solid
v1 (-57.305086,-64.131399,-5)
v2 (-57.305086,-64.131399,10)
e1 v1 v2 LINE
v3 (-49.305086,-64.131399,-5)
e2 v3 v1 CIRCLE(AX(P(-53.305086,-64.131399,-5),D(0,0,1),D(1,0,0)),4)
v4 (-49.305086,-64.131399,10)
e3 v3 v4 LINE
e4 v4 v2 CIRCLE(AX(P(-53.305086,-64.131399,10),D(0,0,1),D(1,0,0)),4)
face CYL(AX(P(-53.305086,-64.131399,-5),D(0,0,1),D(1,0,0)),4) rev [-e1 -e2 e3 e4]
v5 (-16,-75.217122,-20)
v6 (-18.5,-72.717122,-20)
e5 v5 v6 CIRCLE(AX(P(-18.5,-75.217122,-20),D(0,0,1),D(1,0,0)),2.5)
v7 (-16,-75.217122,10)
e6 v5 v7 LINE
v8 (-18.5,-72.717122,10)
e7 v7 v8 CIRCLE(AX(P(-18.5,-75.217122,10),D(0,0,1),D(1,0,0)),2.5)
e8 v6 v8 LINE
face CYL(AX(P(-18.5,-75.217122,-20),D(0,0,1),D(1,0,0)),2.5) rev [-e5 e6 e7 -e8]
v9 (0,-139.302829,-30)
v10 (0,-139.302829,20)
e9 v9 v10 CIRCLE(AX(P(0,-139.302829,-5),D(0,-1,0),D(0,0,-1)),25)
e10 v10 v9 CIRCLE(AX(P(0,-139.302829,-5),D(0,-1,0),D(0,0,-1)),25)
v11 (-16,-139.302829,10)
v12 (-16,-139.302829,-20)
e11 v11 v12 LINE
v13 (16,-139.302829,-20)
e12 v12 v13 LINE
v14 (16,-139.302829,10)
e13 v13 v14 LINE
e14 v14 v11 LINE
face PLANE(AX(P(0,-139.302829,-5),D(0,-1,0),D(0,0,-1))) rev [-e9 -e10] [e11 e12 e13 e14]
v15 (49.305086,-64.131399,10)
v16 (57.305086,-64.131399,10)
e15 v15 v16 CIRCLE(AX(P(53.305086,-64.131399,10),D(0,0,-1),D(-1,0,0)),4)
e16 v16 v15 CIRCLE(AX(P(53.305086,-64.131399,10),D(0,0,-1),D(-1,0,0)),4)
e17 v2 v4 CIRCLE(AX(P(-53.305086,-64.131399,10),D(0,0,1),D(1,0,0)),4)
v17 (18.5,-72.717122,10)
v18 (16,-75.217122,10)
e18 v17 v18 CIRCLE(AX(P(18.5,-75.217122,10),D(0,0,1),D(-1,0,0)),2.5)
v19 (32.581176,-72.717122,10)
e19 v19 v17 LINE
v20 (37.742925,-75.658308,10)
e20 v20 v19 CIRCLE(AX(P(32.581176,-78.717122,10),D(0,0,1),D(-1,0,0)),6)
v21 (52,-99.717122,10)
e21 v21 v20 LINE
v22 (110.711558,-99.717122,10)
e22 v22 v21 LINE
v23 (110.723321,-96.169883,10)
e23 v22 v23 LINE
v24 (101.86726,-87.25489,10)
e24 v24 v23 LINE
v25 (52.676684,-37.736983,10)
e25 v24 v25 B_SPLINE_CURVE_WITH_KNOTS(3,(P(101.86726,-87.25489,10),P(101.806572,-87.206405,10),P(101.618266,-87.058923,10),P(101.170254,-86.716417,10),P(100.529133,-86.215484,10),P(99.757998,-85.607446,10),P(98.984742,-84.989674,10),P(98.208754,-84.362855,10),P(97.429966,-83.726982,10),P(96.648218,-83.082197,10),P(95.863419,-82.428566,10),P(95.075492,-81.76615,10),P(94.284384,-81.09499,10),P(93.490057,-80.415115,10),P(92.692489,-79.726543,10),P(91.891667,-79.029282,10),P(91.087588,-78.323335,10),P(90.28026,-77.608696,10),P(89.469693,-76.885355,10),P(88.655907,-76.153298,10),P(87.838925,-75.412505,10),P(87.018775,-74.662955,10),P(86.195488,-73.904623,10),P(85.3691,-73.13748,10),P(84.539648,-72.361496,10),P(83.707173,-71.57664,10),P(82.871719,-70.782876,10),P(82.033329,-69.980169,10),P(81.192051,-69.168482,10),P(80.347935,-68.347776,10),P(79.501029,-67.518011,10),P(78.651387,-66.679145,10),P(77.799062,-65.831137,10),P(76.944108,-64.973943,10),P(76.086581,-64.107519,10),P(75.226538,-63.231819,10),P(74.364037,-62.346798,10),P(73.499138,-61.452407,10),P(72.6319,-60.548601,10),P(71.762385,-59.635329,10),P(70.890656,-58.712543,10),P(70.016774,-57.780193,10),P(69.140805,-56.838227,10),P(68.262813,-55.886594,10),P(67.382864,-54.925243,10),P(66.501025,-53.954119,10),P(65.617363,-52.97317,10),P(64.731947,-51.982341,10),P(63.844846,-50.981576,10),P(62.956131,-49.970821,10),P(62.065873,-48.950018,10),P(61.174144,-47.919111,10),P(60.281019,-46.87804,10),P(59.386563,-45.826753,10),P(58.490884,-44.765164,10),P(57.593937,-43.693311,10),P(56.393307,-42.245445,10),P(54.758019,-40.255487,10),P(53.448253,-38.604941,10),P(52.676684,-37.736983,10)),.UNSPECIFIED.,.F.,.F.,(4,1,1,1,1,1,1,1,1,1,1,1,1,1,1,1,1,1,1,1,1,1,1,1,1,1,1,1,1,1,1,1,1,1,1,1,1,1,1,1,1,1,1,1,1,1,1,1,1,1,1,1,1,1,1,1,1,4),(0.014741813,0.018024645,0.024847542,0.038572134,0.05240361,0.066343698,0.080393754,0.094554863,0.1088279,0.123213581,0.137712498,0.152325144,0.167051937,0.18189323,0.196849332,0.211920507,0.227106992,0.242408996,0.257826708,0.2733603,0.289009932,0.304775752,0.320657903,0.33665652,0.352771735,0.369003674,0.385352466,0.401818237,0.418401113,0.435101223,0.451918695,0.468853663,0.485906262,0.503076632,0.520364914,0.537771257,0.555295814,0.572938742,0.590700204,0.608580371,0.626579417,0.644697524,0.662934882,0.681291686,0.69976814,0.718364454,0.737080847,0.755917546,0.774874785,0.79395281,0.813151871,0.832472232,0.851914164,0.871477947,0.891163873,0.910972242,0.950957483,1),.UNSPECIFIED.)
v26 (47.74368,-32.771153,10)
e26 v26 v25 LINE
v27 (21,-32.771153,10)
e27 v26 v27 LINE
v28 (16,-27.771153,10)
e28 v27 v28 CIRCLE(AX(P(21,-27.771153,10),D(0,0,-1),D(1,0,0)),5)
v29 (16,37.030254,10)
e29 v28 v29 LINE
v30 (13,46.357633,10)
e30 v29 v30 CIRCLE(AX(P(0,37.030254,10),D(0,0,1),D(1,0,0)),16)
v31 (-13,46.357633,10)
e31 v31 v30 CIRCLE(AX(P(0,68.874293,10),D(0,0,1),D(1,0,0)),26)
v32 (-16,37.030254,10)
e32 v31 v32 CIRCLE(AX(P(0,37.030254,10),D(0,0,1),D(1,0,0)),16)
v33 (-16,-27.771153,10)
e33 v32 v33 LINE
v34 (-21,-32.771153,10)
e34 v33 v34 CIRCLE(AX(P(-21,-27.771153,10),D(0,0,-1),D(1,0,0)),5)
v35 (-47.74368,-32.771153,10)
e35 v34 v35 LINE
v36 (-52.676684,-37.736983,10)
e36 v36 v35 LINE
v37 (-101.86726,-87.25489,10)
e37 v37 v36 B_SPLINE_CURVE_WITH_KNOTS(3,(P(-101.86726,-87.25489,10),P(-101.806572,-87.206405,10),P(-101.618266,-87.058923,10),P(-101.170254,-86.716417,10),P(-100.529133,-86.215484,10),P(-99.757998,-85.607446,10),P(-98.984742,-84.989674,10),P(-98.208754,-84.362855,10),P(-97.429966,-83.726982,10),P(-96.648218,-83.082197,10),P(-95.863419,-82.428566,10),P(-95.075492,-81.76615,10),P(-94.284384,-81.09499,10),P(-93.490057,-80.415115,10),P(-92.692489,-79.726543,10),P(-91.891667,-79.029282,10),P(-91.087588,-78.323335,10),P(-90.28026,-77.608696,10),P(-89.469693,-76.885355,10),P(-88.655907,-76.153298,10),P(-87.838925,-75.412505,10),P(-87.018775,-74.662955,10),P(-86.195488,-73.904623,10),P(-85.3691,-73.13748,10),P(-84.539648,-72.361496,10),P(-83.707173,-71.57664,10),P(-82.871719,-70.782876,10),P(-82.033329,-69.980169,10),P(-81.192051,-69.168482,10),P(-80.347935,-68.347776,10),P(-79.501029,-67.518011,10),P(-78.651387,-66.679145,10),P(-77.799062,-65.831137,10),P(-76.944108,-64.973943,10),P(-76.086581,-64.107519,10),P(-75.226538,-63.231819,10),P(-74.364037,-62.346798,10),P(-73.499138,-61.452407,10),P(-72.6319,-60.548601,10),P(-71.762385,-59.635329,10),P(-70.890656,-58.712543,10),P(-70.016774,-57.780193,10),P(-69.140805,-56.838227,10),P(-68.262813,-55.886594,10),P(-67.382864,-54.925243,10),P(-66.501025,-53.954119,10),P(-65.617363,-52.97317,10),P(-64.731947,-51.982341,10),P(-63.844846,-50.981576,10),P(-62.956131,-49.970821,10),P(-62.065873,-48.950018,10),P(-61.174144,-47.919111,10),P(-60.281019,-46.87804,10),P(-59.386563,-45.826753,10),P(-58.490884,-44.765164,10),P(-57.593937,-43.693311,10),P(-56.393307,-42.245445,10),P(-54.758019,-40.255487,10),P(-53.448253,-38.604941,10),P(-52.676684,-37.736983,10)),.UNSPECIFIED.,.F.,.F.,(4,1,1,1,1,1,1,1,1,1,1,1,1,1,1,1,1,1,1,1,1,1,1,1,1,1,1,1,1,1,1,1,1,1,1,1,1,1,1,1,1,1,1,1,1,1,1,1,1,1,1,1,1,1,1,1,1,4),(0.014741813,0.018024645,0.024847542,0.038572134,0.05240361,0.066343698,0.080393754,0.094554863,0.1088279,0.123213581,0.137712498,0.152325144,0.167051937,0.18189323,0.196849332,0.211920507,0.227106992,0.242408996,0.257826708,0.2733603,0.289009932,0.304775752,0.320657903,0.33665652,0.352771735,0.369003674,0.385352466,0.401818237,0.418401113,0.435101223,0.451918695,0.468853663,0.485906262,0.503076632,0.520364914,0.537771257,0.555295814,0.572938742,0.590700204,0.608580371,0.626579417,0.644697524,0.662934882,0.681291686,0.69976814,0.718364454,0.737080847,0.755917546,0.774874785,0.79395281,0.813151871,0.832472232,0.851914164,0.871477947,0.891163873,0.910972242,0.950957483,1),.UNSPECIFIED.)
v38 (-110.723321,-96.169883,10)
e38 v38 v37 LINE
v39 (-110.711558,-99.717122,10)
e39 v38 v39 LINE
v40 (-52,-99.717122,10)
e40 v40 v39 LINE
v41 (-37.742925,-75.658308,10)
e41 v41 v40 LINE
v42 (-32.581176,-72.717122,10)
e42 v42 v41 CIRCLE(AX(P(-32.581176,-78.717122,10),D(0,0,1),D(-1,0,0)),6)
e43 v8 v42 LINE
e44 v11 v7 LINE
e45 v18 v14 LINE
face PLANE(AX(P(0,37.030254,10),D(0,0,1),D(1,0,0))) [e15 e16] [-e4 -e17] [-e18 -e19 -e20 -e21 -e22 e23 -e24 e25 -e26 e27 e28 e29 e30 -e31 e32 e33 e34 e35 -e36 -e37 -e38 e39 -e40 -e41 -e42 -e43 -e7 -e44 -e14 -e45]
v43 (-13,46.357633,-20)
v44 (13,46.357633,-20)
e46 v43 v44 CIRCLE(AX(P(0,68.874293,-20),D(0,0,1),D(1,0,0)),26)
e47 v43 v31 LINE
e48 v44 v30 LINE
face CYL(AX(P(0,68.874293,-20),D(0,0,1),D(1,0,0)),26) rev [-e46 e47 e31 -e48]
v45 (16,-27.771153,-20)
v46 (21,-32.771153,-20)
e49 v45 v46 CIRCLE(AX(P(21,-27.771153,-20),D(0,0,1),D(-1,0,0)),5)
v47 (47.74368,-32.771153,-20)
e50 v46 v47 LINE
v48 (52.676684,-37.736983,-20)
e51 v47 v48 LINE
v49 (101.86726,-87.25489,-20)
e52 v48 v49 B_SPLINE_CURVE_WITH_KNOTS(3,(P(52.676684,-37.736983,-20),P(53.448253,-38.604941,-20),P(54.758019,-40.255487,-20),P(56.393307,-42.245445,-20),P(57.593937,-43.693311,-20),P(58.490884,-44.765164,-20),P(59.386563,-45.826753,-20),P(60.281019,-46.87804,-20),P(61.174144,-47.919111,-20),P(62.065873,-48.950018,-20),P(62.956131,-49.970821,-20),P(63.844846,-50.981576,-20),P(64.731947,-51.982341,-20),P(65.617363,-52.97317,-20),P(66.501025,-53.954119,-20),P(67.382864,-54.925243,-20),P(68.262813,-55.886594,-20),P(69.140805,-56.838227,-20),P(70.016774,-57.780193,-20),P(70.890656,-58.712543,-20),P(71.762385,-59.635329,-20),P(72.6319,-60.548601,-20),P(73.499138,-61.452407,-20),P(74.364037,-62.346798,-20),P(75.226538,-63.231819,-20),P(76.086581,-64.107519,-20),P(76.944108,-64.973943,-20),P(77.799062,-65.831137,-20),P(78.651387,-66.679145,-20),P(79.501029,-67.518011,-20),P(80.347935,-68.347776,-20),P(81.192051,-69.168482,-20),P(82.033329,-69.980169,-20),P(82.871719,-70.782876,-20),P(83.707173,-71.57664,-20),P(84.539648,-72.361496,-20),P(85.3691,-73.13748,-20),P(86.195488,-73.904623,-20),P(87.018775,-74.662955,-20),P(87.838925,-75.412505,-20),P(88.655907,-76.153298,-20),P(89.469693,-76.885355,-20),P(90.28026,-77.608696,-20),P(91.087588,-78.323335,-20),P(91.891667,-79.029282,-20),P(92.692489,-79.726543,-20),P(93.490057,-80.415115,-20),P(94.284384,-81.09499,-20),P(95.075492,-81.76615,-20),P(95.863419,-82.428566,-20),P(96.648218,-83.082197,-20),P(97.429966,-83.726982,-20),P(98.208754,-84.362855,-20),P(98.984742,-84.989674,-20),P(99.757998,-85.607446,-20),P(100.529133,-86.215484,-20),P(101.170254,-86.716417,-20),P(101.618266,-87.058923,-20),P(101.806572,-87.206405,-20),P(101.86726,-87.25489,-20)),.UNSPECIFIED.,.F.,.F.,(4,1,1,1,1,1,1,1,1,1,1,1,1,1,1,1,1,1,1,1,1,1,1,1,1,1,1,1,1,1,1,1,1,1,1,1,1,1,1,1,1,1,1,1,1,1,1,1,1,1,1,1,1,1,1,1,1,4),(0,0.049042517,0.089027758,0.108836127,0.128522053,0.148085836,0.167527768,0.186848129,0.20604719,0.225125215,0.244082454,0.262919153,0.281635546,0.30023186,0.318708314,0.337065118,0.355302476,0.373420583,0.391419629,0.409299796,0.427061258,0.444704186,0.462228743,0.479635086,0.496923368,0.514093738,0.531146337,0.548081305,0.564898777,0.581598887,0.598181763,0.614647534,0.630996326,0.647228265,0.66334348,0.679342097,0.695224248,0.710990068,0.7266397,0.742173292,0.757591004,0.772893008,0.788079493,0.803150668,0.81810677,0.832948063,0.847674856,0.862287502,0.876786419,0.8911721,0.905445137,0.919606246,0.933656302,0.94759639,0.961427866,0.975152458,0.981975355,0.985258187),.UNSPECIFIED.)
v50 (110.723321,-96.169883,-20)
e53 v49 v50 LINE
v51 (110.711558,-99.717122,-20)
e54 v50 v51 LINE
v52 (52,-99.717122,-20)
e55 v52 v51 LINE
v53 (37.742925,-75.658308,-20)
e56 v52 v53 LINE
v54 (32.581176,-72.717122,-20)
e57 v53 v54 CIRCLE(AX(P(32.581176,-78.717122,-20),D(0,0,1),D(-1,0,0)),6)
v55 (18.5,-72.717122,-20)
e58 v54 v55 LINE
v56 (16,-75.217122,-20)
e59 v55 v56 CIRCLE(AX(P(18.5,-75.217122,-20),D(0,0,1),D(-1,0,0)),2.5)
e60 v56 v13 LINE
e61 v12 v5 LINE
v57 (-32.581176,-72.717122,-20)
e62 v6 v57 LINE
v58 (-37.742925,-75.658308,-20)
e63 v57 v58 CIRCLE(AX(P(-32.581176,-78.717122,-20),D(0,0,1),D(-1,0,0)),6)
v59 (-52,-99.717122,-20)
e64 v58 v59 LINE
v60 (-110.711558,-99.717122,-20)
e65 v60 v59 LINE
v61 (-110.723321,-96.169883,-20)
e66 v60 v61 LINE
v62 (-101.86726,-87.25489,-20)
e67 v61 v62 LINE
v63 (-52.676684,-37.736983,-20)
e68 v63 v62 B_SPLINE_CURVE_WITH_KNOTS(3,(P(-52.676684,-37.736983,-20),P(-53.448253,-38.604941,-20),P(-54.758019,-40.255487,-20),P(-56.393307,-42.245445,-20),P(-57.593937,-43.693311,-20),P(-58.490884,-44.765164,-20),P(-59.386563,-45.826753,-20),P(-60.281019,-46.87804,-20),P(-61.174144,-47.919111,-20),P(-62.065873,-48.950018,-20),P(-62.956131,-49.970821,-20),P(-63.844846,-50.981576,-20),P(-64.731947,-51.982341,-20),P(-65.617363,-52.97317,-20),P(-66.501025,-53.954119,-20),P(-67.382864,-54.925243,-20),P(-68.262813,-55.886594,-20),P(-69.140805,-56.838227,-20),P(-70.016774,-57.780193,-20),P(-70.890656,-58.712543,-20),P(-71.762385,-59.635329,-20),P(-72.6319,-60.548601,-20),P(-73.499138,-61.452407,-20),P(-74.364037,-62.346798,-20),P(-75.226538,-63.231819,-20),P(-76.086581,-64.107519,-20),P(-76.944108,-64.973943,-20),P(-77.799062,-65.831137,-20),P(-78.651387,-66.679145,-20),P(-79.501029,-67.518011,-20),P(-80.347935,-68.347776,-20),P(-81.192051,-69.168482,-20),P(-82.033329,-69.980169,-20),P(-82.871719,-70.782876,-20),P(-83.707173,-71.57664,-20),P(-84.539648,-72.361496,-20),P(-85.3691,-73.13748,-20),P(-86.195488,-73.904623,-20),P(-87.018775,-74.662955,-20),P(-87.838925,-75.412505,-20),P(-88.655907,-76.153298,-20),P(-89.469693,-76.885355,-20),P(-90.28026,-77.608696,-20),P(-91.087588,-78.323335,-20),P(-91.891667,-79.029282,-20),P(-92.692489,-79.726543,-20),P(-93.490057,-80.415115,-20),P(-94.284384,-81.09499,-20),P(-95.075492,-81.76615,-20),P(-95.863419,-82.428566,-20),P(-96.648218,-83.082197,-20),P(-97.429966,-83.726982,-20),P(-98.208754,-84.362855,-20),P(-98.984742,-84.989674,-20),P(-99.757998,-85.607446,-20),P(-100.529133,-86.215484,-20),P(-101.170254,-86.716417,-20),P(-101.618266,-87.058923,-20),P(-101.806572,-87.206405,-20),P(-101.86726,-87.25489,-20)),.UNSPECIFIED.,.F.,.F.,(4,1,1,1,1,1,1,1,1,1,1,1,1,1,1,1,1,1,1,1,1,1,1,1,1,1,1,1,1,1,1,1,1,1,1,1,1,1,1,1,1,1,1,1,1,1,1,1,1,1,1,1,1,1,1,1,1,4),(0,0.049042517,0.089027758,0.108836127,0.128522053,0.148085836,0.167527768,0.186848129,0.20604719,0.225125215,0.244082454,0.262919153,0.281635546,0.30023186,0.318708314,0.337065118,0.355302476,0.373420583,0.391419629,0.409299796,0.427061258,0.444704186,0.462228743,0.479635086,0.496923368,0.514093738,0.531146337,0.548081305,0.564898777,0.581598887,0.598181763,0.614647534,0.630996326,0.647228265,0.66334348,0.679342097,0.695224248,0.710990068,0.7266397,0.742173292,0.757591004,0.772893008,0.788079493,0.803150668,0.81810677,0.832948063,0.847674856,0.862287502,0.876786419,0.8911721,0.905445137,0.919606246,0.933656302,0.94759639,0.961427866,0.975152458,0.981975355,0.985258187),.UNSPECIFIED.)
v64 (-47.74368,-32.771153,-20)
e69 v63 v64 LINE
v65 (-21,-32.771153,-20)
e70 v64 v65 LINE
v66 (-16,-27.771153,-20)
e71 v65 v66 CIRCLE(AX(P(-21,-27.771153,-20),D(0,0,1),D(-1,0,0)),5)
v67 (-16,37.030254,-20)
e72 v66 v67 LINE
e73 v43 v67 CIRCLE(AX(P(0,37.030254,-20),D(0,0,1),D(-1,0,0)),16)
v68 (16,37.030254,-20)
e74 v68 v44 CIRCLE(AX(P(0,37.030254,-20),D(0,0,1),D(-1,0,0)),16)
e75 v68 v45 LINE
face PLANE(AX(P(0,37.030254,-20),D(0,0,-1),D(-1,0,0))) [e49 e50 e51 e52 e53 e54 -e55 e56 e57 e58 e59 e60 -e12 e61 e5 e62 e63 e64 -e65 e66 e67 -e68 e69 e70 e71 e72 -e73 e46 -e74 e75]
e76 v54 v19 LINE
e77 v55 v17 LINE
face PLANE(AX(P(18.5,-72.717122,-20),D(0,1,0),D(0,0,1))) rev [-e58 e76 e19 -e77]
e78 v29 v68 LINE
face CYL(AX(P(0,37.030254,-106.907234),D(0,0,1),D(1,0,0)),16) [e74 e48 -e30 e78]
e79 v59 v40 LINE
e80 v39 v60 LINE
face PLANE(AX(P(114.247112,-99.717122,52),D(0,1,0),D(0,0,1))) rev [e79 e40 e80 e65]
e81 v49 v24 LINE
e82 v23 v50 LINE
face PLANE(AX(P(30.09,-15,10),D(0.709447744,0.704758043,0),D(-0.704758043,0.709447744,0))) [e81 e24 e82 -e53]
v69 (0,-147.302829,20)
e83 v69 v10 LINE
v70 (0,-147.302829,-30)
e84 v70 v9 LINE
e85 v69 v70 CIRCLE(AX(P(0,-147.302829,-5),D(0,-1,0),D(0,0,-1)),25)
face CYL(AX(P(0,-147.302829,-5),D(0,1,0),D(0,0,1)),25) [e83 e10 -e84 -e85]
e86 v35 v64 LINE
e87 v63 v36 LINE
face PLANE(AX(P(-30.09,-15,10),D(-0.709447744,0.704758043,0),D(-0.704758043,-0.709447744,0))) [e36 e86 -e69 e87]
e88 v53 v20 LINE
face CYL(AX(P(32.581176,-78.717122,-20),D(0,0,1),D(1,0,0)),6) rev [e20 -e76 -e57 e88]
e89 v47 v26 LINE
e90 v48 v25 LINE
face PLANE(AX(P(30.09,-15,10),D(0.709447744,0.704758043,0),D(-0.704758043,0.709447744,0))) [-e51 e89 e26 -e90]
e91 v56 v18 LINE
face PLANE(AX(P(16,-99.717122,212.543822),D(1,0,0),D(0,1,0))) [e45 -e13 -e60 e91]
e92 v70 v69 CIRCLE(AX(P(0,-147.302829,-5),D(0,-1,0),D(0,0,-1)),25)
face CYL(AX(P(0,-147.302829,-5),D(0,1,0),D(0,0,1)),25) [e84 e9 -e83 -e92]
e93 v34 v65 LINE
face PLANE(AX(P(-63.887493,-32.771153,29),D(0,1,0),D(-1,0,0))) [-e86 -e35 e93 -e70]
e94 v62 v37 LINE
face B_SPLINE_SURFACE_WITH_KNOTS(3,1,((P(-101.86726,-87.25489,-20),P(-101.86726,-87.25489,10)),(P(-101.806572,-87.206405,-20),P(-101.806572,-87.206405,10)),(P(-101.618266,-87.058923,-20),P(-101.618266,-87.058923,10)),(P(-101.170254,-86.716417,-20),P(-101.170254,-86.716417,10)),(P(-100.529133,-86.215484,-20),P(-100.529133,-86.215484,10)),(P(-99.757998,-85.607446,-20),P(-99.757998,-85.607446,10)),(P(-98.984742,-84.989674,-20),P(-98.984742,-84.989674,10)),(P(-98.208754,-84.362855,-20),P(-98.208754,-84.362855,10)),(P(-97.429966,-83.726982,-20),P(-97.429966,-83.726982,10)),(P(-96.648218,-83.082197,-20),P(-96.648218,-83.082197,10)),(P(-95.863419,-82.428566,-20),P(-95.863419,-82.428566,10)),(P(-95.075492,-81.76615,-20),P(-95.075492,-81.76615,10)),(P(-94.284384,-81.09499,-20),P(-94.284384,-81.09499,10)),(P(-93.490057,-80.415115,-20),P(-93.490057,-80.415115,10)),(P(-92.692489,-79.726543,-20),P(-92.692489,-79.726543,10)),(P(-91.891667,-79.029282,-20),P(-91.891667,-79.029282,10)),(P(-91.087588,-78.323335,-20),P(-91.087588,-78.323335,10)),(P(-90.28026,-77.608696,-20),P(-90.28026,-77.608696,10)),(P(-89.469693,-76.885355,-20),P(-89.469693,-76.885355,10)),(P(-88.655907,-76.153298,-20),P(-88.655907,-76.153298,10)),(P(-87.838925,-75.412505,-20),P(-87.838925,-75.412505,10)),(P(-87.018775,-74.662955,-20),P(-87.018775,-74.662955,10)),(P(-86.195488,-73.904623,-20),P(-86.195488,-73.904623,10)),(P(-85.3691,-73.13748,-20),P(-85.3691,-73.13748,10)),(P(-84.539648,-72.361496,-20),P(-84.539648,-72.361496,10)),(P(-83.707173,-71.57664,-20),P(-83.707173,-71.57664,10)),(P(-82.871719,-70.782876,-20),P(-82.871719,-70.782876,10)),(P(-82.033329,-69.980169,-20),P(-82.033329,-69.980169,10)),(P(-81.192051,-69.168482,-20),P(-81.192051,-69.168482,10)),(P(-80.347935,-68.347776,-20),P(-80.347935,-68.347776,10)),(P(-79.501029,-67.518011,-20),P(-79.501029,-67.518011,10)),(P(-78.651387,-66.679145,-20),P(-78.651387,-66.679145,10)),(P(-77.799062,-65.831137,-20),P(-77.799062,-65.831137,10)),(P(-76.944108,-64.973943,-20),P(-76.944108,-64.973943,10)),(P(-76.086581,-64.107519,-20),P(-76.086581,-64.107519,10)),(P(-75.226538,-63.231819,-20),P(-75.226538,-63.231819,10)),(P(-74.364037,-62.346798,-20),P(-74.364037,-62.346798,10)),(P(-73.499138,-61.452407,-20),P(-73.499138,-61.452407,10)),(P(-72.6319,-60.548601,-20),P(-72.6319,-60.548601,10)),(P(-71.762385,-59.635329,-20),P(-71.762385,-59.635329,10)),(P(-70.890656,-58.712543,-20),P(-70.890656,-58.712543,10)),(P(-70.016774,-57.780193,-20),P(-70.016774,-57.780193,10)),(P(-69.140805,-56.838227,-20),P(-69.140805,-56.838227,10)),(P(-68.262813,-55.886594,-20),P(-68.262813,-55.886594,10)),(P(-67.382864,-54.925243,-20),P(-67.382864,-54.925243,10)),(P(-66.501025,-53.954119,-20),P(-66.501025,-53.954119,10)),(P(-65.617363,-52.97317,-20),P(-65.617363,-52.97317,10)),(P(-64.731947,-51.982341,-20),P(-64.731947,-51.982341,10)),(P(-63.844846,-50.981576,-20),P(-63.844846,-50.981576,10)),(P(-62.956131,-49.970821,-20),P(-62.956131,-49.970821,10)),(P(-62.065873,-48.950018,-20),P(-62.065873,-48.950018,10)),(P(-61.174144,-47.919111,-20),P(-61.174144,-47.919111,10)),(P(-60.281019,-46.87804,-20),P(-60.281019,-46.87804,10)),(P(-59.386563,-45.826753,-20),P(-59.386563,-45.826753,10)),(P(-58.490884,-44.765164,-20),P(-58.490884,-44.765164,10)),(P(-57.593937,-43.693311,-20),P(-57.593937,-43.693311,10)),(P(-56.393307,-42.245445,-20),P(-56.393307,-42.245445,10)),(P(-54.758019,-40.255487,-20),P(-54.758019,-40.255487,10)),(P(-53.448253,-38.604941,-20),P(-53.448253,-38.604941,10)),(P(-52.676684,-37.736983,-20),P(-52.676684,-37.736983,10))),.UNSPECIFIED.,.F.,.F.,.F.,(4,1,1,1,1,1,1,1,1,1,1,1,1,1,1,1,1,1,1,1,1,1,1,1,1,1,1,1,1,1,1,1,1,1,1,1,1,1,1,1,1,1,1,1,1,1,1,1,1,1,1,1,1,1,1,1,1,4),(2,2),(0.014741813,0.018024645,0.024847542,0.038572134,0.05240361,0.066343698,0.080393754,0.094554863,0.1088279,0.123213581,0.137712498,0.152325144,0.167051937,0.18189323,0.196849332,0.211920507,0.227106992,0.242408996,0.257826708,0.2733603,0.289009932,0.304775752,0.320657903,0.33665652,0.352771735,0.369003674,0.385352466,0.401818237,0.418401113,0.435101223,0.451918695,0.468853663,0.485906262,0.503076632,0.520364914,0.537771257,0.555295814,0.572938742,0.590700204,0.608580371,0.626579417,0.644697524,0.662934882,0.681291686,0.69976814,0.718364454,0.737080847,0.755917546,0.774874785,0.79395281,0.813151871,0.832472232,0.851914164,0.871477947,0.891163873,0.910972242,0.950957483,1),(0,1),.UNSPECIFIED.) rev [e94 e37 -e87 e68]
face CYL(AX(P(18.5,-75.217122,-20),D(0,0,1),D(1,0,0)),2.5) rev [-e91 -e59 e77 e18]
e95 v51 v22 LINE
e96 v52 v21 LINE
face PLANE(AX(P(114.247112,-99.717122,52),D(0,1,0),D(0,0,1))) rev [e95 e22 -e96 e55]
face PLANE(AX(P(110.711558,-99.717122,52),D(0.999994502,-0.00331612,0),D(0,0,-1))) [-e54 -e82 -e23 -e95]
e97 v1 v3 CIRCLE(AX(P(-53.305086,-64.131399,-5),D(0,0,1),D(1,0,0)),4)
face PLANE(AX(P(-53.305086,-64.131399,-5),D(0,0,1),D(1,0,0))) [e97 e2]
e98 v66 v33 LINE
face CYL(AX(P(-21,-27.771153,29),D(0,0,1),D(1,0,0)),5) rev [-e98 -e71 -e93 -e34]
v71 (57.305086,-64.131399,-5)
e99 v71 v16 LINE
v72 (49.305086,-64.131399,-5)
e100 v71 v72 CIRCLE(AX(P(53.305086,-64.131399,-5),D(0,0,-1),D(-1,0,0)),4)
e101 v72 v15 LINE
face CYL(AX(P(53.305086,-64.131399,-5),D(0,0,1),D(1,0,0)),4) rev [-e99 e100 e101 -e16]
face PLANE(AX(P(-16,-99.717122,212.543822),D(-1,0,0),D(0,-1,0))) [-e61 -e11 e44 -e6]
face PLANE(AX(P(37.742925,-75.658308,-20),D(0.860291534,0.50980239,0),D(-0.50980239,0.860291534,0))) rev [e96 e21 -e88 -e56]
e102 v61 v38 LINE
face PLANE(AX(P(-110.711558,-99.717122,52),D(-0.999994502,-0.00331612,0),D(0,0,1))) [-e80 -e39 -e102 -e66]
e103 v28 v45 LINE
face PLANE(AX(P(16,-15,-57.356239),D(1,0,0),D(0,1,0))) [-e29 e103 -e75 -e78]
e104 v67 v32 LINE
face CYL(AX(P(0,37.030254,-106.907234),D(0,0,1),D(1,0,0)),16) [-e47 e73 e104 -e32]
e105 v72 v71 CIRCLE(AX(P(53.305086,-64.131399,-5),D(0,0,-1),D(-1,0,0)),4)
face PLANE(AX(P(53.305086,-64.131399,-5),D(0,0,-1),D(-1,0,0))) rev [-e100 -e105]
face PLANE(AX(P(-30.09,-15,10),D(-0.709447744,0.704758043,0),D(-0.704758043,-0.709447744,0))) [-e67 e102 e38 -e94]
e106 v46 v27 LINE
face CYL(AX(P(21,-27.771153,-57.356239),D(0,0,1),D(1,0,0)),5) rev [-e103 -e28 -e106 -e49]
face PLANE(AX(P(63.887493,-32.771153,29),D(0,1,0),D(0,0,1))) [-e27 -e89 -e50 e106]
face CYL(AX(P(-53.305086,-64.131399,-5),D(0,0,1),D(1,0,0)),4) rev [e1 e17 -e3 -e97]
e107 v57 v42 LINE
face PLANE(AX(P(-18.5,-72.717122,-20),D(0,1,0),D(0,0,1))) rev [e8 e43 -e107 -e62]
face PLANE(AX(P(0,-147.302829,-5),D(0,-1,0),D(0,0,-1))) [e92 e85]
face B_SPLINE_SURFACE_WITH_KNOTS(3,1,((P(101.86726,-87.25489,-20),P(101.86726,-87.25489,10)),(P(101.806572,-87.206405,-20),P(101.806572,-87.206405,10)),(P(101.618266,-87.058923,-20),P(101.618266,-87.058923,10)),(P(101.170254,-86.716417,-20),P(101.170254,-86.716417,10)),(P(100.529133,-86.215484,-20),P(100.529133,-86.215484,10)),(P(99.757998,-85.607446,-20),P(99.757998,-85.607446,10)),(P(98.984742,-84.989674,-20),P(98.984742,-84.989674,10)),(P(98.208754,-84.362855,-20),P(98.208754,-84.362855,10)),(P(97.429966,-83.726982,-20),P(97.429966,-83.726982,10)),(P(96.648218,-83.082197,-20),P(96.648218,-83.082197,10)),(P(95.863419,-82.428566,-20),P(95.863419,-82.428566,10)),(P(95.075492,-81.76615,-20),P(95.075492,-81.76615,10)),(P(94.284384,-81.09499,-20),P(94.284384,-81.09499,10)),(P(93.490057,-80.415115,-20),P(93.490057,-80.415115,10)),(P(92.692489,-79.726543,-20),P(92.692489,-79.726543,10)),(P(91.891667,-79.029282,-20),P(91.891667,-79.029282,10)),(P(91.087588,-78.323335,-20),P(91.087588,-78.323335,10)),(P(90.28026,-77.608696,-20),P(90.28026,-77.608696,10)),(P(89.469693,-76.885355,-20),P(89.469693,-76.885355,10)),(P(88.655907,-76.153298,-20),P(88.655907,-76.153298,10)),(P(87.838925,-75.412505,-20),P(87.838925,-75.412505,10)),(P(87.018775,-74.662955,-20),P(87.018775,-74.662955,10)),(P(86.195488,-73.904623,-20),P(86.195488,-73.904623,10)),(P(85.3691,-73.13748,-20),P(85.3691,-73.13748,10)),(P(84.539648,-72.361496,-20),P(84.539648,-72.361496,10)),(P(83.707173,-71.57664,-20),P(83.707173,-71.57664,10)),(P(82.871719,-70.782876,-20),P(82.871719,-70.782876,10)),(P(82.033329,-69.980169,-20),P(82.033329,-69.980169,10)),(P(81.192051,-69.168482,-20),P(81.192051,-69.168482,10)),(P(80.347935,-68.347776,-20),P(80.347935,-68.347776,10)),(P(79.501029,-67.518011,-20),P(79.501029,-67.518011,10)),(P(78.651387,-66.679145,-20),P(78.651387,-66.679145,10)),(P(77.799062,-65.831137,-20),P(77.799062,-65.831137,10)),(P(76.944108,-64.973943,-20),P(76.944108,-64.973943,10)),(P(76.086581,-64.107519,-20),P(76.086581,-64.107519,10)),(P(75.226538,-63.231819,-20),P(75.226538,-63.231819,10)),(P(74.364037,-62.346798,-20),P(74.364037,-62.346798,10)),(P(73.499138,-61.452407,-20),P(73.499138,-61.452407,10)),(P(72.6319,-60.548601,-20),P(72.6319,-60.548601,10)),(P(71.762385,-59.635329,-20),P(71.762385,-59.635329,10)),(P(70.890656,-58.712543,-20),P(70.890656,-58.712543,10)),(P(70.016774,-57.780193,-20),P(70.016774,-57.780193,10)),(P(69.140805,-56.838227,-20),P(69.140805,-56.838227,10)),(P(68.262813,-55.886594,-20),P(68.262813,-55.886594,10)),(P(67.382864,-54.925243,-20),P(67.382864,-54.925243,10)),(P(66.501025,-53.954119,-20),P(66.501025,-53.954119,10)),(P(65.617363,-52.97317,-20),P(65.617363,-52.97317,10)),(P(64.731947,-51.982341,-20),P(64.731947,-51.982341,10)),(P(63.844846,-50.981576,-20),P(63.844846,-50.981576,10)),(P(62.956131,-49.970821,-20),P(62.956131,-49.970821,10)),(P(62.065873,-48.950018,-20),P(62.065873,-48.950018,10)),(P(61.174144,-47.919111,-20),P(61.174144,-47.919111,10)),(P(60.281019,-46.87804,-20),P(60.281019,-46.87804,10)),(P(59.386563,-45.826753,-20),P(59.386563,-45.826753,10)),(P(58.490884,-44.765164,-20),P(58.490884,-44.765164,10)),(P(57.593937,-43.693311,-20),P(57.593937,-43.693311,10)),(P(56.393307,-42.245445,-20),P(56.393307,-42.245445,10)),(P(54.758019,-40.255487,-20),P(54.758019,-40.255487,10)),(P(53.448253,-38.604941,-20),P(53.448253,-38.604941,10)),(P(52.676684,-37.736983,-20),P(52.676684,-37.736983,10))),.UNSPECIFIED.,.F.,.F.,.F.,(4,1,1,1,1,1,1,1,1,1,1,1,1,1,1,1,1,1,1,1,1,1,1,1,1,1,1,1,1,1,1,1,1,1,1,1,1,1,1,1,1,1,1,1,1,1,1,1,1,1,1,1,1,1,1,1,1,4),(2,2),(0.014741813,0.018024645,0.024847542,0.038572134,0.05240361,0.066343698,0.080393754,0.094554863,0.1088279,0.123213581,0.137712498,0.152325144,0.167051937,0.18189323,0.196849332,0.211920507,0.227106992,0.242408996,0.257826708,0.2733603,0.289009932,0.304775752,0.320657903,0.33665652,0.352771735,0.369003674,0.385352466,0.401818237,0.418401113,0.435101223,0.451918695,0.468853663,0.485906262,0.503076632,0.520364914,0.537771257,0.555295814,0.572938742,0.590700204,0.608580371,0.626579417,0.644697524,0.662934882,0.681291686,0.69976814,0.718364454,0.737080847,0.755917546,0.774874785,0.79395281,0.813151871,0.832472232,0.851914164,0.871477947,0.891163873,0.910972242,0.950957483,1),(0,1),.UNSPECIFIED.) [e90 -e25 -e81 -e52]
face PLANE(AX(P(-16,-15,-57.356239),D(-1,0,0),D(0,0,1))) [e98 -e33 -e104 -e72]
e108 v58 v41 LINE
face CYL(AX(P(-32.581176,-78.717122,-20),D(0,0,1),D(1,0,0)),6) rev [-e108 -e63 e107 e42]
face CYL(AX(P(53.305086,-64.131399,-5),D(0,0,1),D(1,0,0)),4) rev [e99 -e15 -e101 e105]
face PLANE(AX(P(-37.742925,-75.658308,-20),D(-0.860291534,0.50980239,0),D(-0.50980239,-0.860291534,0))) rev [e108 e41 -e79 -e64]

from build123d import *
from OCP.BRepFilletAPI import BRepFilletAPI_MakeChamfer

# Parameters (mm, degrees)
BOSS_EXTRUDE1_DEPTH      = 10
BOSS_EXTRUDE2_DEPTH      = 10
SKETCH72_R               = 5
CUT_EXTRUDE2_DEPTH       = 10
CUT_EXTRUDE4_DEPTH       = 14
CUT_EXTRUDE4_DEPTH_BACK  = 19
BOSS_EXTRUDE3_START      = 20
BOSS_EXTRUDE3_DEPTH      = 20
CUT_EXTRUDE5_DEPTH       = 19
CUT_EXTRUDE5_DEPTH_BACK  = 48
SKETCH146_R              = 5
CUT_EXTRUDE6_DEPTH       = 19
CUT_EXTRUDE6_DEPTH_BACK  = 19
CUT_EXTRUDE7_DEPTH       = 60
CUT_EXTRUDE8_DEPTH       = 72
CUT_EXTRUDE9_DEPTH       = 88
BOSS_EXTRUDE6_START      = -7.5
BOSS_EXTRUDE6_DEPTH      = 7.5
CUT_EXTRUDE10_DEPTH      = 19
CUT_EXTRUDE10_DEPTH_BACK = 41
SKETCH171_R              = 5
BOSS_EXTRUDE7_DEPTH      = 7.5
SKETCH172_W              = 3
SKETCH172_H              = 35.030253814
BOSS_EXTRUDE8_DEPTH      = 15
SKETCH173_W              = 32
SKETCH173_H              = 200
BOSS_EXTRUDE9_DEPTH      = 30
CHAMFER1_SIZE            = 5
CHAMFER1_SIZE2           = 3.535553346
FILLET1_R                = 5
CUT_EXTRUDE11_DEPTH      = 30
SKETCH175_W              = 47.76869264
SKETCH175_H              = 185.151923251
CUT_EXTRUDE12_DEPTH      = 55
SKETCH151_R              = 4
CUT_EXTRUDE14_DEPTH      = 15
SKETCH153_R              = 4
CUT_EXTRUDE15_DEPTH      = 15
CHAMFER3_SIZE            = 0.5
BOSS_EXTRUDE10_DEPTH     = 30
CUT_EXTRUDE16_DEPTH      = 181.457563316
SKETCH179_R              = 25
BOSS_EXTRUDE11_DEPTH     = 8


with BuildPart() as part:
    # Sketch1 → Boss-Extrude1 (new body)
    with BuildSketch(Plane.XY):
        with BuildLine():
            Line((-15, 37.030253814), (-15, -127.65801455))
            Line((-15, -127.65801455), (15, -127.65801455))
            Line((15, -127.65801455), (15, 37.030253814))
            ThreePointArc((15, 37.030253814), (0, 52.030253814), (-15, 37.030253814))
        make_face()
    extrude(amount=BOSS_EXTRUDE1_DEPTH)

    # Sketch2 → Boss-Extrude2 (add)
    with BuildSketch(Plane(origin=(0, 0, 0), x_dir=(-1, 0, 0), z_dir=(0, 0, -1))):
        Polygon((0, -15), (30.09, -15), (139.247111701, -124.883480474), (-139.247111701, -124.883480474), (-30.09, -15), align=None)
    extrude(amount=-BOSS_EXTRUDE2_DEPTH)

    # Sketch72 → Cut-Extrude2 (cut)
    with BuildSketch(Plane.XY.offset(10)):
        with Locations((0, 37.030253814)):
            Circle(SKETCH72_R)
    extrude(amount=-CUT_EXTRUDE2_DEPTH, mode=Mode.SUBTRACT)

    # Sketch144 → Cut-Extrude4 (cut, two sides: drawn at the far end of the back side and taken through both)
    with BuildSketch(Plane.XY.offset(10).offset(-CUT_EXTRUDE4_DEPTH_BACK)):
        with BuildLine():
            Line((-13, 37.030253814), (-13, -15))
            Line((-13, -15), (-23, -15))
            Line((-23, -15), (-23, 37.030253814))
            ThreePointArc((-23, 37.030253814), (0, 60.030253814), (23, 37.030253814))
            Line((23, 37.030253814), (23, -15))
            Line((23, -15), (13, -15))
            Line((13, -15), (13, 37.030253814))
            ThreePointArc((13, 37.030253814), (0, 50.030253814), (-13, 37.030253814))
        make_face()
    extrude(amount=CUT_EXTRUDE4_DEPTH + CUT_EXTRUDE4_DEPTH_BACK, mode=Mode.SUBTRACT)

    # Sketch145 → Boss-Extrude3 (add)
    with BuildSketch(Plane(origin=(0, 0, 0), x_dir=(-1, 0, 0), z_dir=(0, 0, -1)).offset(BOSS_EXTRUDE3_START)):
        with BuildLine():
            Line((30.09, -15), (13, -15))
            Line((13, -15), (13, 37.030253814))
            ThreePointArc((13, 37.030253814), (0, 50.030253814), (-13, 37.030253814))
            Line((-13, 37.030253814), (-13, -15))
            Line((-13, -15), (-30.09, -15))
            Line((-30.09, -15), (-139.247111701, -124.883480474))
            Line((-139.247111701, -124.883480474), (-15, -124.883480474))
            Line((-15, -124.883480474), (-15, -127.65801455))
            Line((-15, -127.65801455), (15, -127.65801455))
            Line((15, -127.65801455), (15, -124.883480474))
            Line((15, -124.883480474), (139.247111701, -124.883480474))
            Line((139.247111701, -124.883480474), (30.09, -15))
        make_face()
    extrude(amount=-BOSS_EXTRUDE3_DEPTH)

    # Sketch146 → Cut-Extrude5 (cut, two sides: drawn at the far end of the back side and taken through both)
    with BuildSketch(Plane.XY.offset(-CUT_EXTRUDE5_DEPTH_BACK)):
        with Locations((0, 37.030253814)):
            Circle(SKETCH146_R)
    extrude(amount=CUT_EXTRUDE5_DEPTH + CUT_EXTRUDE5_DEPTH_BACK, mode=Mode.SUBTRACT)

    # Sketch147 → Cut-Extrude6 (cut, two sides: drawn at the far end of the back side and taken through both)
    with BuildSketch(Plane(origin=(0, 0, 0), x_dir=(0, 0, -1), z_dir=(1, 0, 0)).offset(-CUT_EXTRUDE6_DEPTH_BACK)):
        Polygon((-2.5, 50.030253814), (-2.5, 20.030253814), (12.5, 20.030253814), (12.5, 50.030253814), (5, 50.030253814), align=None)
    extrude(amount=CUT_EXTRUDE6_DEPTH + CUT_EXTRUDE6_DEPTH_BACK, mode=Mode.SUBTRACT)

    # Sketch150 → Cut-Extrude7 (cut)
    with BuildSketch(Plane.XY.offset(10)):
        Polygon((-139.247111701, -124.883480474), (-114.247111701, -124.883480474), (-114.247111701, -93.838923463), (-155.604312259, -93.838923463), align=None)
        Polygon((139.247111701, -124.883480474), (114.247111701, -124.883480474), (114.247111701, -93.838923463), (144.778818184, -93.838923463), align=None)
    extrude(amount=-CUT_EXTRUDE7_DEPTH, mode=Mode.SUBTRACT)

    # Sketch155 → Cut-Extrude8 (cut)
    with BuildSketch(Plane(origin=(0, 0, -20), x_dir=(-1, 0, 0), z_dir=(0, 0, -1))):
        Polygon((-114.247111701, -99.71712192), (114.247111701, -99.71712192), (132.998124018, -127.280721413), (-4.838954003, -174.810748317), (-128.945135363, -139.691339549), align=None)
    extrude(amount=-CUT_EXTRUDE8_DEPTH, mode=Mode.SUBTRACT)

    # Sketch168 → Cut-Extrude9 (cut)
    with BuildSketch(Plane.XY.offset(10)):
        with BuildLine():
            Line((-102.627965354, -87.973722378), (-98.21134674, -23.838785425))
            Line((-98.21134674, -23.838785425), (-52.676683547, -37.736983068))
            add(Edge.make_bspline(
                [(-52.676683547, -37.736983068), (-53.448253243, -38.604940944), (-54.758018803, -40.255486938), (-56.393307349, -42.24544513), (-57.59393724, -43.693311358), (-58.490883563, -44.765164273), (-59.386563239, -45.826752691), (-60.281018922, -46.878039923), (-61.174144179, -47.919111167), (-62.065873359, -48.950018312), (-62.956131171, -49.970821146), (-63.844846057, -50.981576429), (-64.731946625, -51.982340808), (-65.617362588, -52.973170047), (-66.501024502, -53.954119244), (-67.382863834, -54.925242774), (-68.262812936, -55.886594308), (-69.140805058, -56.83822681), (-70.016774341, -57.78019253), (-70.890655834, -58.712543006), (-71.762385492, -59.635329052), (-72.6319002, -60.548600748), (-73.499137782, -61.452407427), (-74.36403703, -62.346797658), (-75.226537723, -63.231819226), (-76.086580666, -64.107519102), (-76.944107728, -64.97394342), (-77.799061885, -65.83113743), (-78.651387281, -66.679145464), (-79.501029286, -67.518010878), (-80.347934579, -68.347775997), (-81.192051232, -69.16848204), (-82.033328819, -69.980169042), (-82.871718537, -70.782875754), (-83.707173346, -71.576639531), (-84.539648144, -72.3614962), (-85.369099962, -73.137479905), (-86.195488195, -73.90462292), (-87.018774882, -74.662955436), (-87.838925031, -75.412505303), (-88.655907003, -76.153297726), (-89.469692983, -76.885354899), (-90.280259527, -77.608695576), (-91.08758824, -78.323334537), (-91.89166658, -79.029281964), (-92.692488851, -79.726542658), (-93.490057409, -80.415115104), (-94.284384181, -81.094990278), (-95.075492456, -81.766150286), (-95.86341948, -82.428566214), (-96.6482185, -83.08219705), (-97.429965937, -83.726982263), (-98.208753829, -84.362854554), (-98.984742254, -84.989673948), (-99.757998209, -85.607446121), (-100.529132919, -86.215484264), (-101.170253751, -86.716417382), (-101.895413536, -87.270801703), (-102.35237684, -87.641445426), (-102.627965354, -87.973722378)],
                knots=[0, 0, 0, 0, 0.049042517, 0.089027758, 0.108836127, 0.128522053, 0.148085836, 0.167527768, 0.186848129, 0.20604719, 0.225125215, 0.244082454, 0.262919153, 0.281635546, 0.30023186, 0.318708314, 0.337065118, 0.355302476, 0.373420583, 0.391419629, 0.409299796, 0.427061258, 0.444704186, 0.462228743, 0.479635086, 0.496923368, 0.514093738, 0.531146337, 0.548081305, 0.564898777, 0.581598887, 0.598181763, 0.614647534, 0.630996326, 0.647228265, 0.66334348, 0.679342097, 0.695224248, 0.710990068, 0.7266397, 0.742173292, 0.757591004, 0.772893008, 0.788079493, 0.803150668, 0.81810677, 0.832948063, 0.847674856, 0.862287502, 0.876786419, 0.8911721, 0.905445137, 0.919606246, 0.933656302, 0.94759639, 0.961427866, 0.975152458, 0.981975355, 1, 1, 1, 1], degree=3))
        make_face()
    cut_extrude9 = extrude(amount=-CUT_EXTRUDE9_DEPTH, mode=Mode.SUBTRACT)

    # Mirror1: Cut-Extrude9 across plane
    add(cut_extrude9.mirror(Plane(origin=(0, 0, 0), x_dir=(0, 0, 1), z_dir=(1, 0, 0))), mode=Mode.SUBTRACT)

    # Sketch169 → Boss-Extrude6 (add)
    with BuildSketch(Plane.XY.offset(10).offset(BOSS_EXTRUDE6_START)):
        with BuildLine():
            Line((-16, -15), (-13, -15))
            Line((-13, -15), (-13, 37.030253814))
            ThreePointArc((-13, 37.030253814), (-12.375631297, 41.010674647), (-10.5625, 44.608749295))
            Line((-10.5625, 44.608749295), (-16, 37.030253814))
            Line((-16, 37.030253814), (-16, -15))
        make_face()
        with BuildLine():
            Line((16, -15), (16, 37.030253814))
            Line((16, 37.030253814), (10.5625, 44.608749295))
            ThreePointArc((10.5625, 44.608749295), (12.375631297, 41.010674647), (13, 37.030253814))
            Line((13, 37.030253814), (13, -15))
            Line((13, -15), (16, -15))
        make_face()
    extrude(amount=BOSS_EXTRUDE6_DEPTH)

    # Sketch170 → Cut-Extrude10 (cut, two sides: drawn at the far end of the back side and taken through both)
    with BuildSketch(Plane.XY.offset(10).offset(-CUT_EXTRUDE10_DEPTH_BACK)):
        Polygon((-63.887492501, -32.771153319), (-27.188421499, -2.740818682), (-16, -2.740818682), (-16, -15), (-16, -32.771153319), align=None)
        Polygon((16, -15), (16, -32.771153319), (63.887492501, -32.771153319), (27.188421499, -2.740818682), (16, -2.740818682), align=None)
    extrude(amount=CUT_EXTRUDE10_DEPTH + CUT_EXTRUDE10_DEPTH_BACK, mode=Mode.SUBTRACT)

    # Sketch171 → Boss-Extrude7 (add)
    with BuildSketch(Plane(origin=(0, 0, -20), x_dir=(-1, 0, 0), z_dir=(0, 0, -1))):
        with BuildLine():
            Line((16, -15), (-16, -15))
            Line((-16, -15), (-16, 37.030253814))
            Line((-16, 37.030253814), (-10.5625, 44.608749295))
            ThreePointArc((-10.5625, 44.608749295), (0, 50.030253814), (10.5625, 44.608749295))
            Line((10.5625, 44.608749295), (16, 37.030253814))
            Line((16, 37.030253814), (16, -15))
        make_face()
        with Locations(Location((0, 37.030253814, 0), (0, 0, 180))):
            Circle(SKETCH171_R, mode=Mode.SUBTRACT)
    extrude(amount=-BOSS_EXTRUDE7_DEPTH)

    # Sketch172 → Boss-Extrude8 (add)
    with BuildSketch(Plane(origin=(0, 0, 2.5), x_dir=(-1, 0, 0), z_dir=(0, 0, -1))):
        with Locations((-14.5, 2.515126907)):
            Rectangle(SKETCH172_W, SKETCH172_H)
        with Locations((14.5, 2.515126907)):
            Rectangle(SKETCH172_W, SKETCH172_H)
    extrude(amount=BOSS_EXTRUDE8_DEPTH)

    # Sketch173 → Boss-Extrude9 (add)
    with BuildSketch(Plane(origin=(0, 0, -20), x_dir=(-1, 0, 0), z_dir=(0, 0, -1))):
        with Locations((0, -199.71712192)):
            Rectangle(SKETCH173_W, SKETCH173_H)
    extrude(amount=-BOSS_EXTRUDE9_DEPTH)

    # Chamfer1: one chamfer whose edges measure the first distance from different faces: ONE call of the kernel's chamfer builder (chamfer() names one face for all edges)
    chamfer1_edges_1 = [part.edges().sort_by_distance(p)[0] for p in [
        (-114.247111701, -99.71712192, -5),
    ]]
    chamfer1_side_1 = [part.faces().sort_by_distance(p)[0] for p in [
        (-108.057185848, -93.486006182, -5),
    ]]
    chamfer1_edges_2 = [part.edges().sort_by_distance(p)[0] for p in [
        (114.247111701, -99.71712192, -5),
    ]]
    chamfer1_side_2 = [part.faces().sort_by_distance(p)[0] for p in [
        (108.057185848, -93.486006182, -5),
    ]]
    chamfer1 = BRepFilletAPI_MakeChamfer(part.part.solid().wrapped)
    for e in chamfer1_edges_1:
        chamfer1.Add(CHAMFER1_SIZE, CHAMFER1_SIZE2, e.wrapped, chamfer1_side_1[0].wrapped)  # the first distance lies on this face
    for e in chamfer1_edges_2:
        chamfer1.Add(CHAMFER1_SIZE, CHAMFER1_SIZE2, e.wrapped, chamfer1_side_2[0].wrapped)  # the first distance lies on this face
    add(Compound.cast(chamfer1.Shape()), mode=Mode.REPLACE)

    # Fillet1
    fillet1_edges = [part.edges().sort_by_distance(p)[0] for p in [
        (-16, -32.771153319, -5),
        (16, -32.771153319, -5),
    ]]
    fillet(fillet1_edges, radius=FILLET1_R)

    # Sketch174 → Cut-Extrude11 (cut)
    with BuildSketch(Plane.XY.offset(10)):
        with BuildLine():
            Line((-16, -99.71712192), (-16, -75.21712192))
            ThreePointArc((-16, -75.21712192), (-16.732233047, -73.449354967), (-18.5, -72.71712192))
            Line((-18.5, -72.71712192), (-32.581175633, -72.71712192))
            ThreePointArc((-32.581175633, -72.71712192), (-35.551622901, -73.504018907), (-37.742924834, -75.658307578))
            Line((-37.742924834, -75.658307578), (-52, -99.71712192))
            Line((-52, -99.71712192), (-16, -99.71712192))
        make_face()
        with BuildLine():
            Line((16, -99.71712192), (52, -99.71712192))
            Line((52, -99.71712192), (37.742924834, -75.658307578))
            ThreePointArc((37.742924834, -75.658307578), (35.551622901, -73.504018907), (32.581175633, -72.71712192))
            Line((32.581175633, -72.71712192), (18.5, -72.71712192))
            ThreePointArc((18.5, -72.71712192), (16.732233047, -73.449354967), (16, -75.21712192))
            Line((16, -75.21712192), (16, -99.71712192))
        make_face()
    extrude(amount=-CUT_EXTRUDE11_DEPTH, mode=Mode.SUBTRACT)

    # Sketch175 → Cut-Extrude12 (cut)
    with BuildSketch(Plane.XY.offset(10)):
        with Locations((-3.11565368, -231.878790674)):
            Rectangle(SKETCH175_W, SKETCH175_H)
    extrude(amount=-CUT_EXTRUDE12_DEPTH, mode=Mode.SUBTRACT)

    # Sketch151 → Cut-Extrude14 (cut)
    with BuildSketch(Plane.XY.offset(10)):
        with Locations((-53.305086147, -64.131398819)):
            Circle(SKETCH151_R)
    extrude(amount=-CUT_EXTRUDE14_DEPTH, mode=Mode.SUBTRACT)

    # Sketch153 → Cut-Extrude15 (cut)
    with BuildSketch(Plane.XY.offset(10)):
        with Locations(Location((53.305086147, -64.131398819, 0), (0, 0, 180))):
            Circle(SKETCH153_R)
    extrude(amount=-CUT_EXTRUDE15_DEPTH, mode=Mode.SUBTRACT)

    # Chamfer3
    chamfer3_edges = [part.edges().sort_by_distance(p)[0] for p in [
        (-5, 37.030253814, 2.5),
        (0, 20.030253814, 2.5),
        (-13.28125, 40.819501555, 2.5),
        (-16, 28.530253814, 2.5),
        (0, 50.030253814, 2.5),
        (13.28125, 40.819501555, 2.5),
        (0, 50.030253814, -12.5),
        (13.28125, 40.819501555, -12.5),
        (-13.28125, 40.819501555, -12.5),
        (16, 28.530253814, 2.5),
        (16, 20.030253814, -5),
        (-16, 20.030253814, -5),
    ]]
    chamfer(chamfer3_edges, length=CHAMFER3_SIZE)

    # Sketch177 → Boss-Extrude10 (add)
    with BuildSketch(Plane.XY.offset(10)):
        with BuildLine():
            Line((-16, 37.030253814), (-16, -27.771153319))
            Line((-16, -27.771153319), (16, -27.771153319))
            Line((16, -27.771153319), (16, 37.030253814))
            ThreePointArc((16, 37.030253814), (0, 53.030253814), (-16, 37.030253814))
        make_face()
    extrude(amount=-BOSS_EXTRUDE10_DEPTH)

    # Sketch178 → Cut-Extrude16 (cut, through all)
    with BuildSketch(Plane.XY.offset(10)):
        with BuildLine():
            Line((0, 68.874293366), (-13, 46.357632868))
            ThreePointArc((-13, 46.357632868), (0, 42.874293366), (13, 46.357632868))
            Line((13, 46.357632868), (0, 68.874293366))
        make_face()
    extrude(amount=-CUT_EXTRUDE16_DEPTH, mode=Mode.SUBTRACT)

    # Sketch179 → Boss-Extrude11 (add)
    with BuildSketch(Plane.XZ.offset(139.302829048)):
        with Locations(Location((0, -5, 0), (0, 0, 270))):
            Circle(SKETCH179_R)
    extrude(amount=BOSS_EXTRUDE11_DEPTH)


solid = part.part
